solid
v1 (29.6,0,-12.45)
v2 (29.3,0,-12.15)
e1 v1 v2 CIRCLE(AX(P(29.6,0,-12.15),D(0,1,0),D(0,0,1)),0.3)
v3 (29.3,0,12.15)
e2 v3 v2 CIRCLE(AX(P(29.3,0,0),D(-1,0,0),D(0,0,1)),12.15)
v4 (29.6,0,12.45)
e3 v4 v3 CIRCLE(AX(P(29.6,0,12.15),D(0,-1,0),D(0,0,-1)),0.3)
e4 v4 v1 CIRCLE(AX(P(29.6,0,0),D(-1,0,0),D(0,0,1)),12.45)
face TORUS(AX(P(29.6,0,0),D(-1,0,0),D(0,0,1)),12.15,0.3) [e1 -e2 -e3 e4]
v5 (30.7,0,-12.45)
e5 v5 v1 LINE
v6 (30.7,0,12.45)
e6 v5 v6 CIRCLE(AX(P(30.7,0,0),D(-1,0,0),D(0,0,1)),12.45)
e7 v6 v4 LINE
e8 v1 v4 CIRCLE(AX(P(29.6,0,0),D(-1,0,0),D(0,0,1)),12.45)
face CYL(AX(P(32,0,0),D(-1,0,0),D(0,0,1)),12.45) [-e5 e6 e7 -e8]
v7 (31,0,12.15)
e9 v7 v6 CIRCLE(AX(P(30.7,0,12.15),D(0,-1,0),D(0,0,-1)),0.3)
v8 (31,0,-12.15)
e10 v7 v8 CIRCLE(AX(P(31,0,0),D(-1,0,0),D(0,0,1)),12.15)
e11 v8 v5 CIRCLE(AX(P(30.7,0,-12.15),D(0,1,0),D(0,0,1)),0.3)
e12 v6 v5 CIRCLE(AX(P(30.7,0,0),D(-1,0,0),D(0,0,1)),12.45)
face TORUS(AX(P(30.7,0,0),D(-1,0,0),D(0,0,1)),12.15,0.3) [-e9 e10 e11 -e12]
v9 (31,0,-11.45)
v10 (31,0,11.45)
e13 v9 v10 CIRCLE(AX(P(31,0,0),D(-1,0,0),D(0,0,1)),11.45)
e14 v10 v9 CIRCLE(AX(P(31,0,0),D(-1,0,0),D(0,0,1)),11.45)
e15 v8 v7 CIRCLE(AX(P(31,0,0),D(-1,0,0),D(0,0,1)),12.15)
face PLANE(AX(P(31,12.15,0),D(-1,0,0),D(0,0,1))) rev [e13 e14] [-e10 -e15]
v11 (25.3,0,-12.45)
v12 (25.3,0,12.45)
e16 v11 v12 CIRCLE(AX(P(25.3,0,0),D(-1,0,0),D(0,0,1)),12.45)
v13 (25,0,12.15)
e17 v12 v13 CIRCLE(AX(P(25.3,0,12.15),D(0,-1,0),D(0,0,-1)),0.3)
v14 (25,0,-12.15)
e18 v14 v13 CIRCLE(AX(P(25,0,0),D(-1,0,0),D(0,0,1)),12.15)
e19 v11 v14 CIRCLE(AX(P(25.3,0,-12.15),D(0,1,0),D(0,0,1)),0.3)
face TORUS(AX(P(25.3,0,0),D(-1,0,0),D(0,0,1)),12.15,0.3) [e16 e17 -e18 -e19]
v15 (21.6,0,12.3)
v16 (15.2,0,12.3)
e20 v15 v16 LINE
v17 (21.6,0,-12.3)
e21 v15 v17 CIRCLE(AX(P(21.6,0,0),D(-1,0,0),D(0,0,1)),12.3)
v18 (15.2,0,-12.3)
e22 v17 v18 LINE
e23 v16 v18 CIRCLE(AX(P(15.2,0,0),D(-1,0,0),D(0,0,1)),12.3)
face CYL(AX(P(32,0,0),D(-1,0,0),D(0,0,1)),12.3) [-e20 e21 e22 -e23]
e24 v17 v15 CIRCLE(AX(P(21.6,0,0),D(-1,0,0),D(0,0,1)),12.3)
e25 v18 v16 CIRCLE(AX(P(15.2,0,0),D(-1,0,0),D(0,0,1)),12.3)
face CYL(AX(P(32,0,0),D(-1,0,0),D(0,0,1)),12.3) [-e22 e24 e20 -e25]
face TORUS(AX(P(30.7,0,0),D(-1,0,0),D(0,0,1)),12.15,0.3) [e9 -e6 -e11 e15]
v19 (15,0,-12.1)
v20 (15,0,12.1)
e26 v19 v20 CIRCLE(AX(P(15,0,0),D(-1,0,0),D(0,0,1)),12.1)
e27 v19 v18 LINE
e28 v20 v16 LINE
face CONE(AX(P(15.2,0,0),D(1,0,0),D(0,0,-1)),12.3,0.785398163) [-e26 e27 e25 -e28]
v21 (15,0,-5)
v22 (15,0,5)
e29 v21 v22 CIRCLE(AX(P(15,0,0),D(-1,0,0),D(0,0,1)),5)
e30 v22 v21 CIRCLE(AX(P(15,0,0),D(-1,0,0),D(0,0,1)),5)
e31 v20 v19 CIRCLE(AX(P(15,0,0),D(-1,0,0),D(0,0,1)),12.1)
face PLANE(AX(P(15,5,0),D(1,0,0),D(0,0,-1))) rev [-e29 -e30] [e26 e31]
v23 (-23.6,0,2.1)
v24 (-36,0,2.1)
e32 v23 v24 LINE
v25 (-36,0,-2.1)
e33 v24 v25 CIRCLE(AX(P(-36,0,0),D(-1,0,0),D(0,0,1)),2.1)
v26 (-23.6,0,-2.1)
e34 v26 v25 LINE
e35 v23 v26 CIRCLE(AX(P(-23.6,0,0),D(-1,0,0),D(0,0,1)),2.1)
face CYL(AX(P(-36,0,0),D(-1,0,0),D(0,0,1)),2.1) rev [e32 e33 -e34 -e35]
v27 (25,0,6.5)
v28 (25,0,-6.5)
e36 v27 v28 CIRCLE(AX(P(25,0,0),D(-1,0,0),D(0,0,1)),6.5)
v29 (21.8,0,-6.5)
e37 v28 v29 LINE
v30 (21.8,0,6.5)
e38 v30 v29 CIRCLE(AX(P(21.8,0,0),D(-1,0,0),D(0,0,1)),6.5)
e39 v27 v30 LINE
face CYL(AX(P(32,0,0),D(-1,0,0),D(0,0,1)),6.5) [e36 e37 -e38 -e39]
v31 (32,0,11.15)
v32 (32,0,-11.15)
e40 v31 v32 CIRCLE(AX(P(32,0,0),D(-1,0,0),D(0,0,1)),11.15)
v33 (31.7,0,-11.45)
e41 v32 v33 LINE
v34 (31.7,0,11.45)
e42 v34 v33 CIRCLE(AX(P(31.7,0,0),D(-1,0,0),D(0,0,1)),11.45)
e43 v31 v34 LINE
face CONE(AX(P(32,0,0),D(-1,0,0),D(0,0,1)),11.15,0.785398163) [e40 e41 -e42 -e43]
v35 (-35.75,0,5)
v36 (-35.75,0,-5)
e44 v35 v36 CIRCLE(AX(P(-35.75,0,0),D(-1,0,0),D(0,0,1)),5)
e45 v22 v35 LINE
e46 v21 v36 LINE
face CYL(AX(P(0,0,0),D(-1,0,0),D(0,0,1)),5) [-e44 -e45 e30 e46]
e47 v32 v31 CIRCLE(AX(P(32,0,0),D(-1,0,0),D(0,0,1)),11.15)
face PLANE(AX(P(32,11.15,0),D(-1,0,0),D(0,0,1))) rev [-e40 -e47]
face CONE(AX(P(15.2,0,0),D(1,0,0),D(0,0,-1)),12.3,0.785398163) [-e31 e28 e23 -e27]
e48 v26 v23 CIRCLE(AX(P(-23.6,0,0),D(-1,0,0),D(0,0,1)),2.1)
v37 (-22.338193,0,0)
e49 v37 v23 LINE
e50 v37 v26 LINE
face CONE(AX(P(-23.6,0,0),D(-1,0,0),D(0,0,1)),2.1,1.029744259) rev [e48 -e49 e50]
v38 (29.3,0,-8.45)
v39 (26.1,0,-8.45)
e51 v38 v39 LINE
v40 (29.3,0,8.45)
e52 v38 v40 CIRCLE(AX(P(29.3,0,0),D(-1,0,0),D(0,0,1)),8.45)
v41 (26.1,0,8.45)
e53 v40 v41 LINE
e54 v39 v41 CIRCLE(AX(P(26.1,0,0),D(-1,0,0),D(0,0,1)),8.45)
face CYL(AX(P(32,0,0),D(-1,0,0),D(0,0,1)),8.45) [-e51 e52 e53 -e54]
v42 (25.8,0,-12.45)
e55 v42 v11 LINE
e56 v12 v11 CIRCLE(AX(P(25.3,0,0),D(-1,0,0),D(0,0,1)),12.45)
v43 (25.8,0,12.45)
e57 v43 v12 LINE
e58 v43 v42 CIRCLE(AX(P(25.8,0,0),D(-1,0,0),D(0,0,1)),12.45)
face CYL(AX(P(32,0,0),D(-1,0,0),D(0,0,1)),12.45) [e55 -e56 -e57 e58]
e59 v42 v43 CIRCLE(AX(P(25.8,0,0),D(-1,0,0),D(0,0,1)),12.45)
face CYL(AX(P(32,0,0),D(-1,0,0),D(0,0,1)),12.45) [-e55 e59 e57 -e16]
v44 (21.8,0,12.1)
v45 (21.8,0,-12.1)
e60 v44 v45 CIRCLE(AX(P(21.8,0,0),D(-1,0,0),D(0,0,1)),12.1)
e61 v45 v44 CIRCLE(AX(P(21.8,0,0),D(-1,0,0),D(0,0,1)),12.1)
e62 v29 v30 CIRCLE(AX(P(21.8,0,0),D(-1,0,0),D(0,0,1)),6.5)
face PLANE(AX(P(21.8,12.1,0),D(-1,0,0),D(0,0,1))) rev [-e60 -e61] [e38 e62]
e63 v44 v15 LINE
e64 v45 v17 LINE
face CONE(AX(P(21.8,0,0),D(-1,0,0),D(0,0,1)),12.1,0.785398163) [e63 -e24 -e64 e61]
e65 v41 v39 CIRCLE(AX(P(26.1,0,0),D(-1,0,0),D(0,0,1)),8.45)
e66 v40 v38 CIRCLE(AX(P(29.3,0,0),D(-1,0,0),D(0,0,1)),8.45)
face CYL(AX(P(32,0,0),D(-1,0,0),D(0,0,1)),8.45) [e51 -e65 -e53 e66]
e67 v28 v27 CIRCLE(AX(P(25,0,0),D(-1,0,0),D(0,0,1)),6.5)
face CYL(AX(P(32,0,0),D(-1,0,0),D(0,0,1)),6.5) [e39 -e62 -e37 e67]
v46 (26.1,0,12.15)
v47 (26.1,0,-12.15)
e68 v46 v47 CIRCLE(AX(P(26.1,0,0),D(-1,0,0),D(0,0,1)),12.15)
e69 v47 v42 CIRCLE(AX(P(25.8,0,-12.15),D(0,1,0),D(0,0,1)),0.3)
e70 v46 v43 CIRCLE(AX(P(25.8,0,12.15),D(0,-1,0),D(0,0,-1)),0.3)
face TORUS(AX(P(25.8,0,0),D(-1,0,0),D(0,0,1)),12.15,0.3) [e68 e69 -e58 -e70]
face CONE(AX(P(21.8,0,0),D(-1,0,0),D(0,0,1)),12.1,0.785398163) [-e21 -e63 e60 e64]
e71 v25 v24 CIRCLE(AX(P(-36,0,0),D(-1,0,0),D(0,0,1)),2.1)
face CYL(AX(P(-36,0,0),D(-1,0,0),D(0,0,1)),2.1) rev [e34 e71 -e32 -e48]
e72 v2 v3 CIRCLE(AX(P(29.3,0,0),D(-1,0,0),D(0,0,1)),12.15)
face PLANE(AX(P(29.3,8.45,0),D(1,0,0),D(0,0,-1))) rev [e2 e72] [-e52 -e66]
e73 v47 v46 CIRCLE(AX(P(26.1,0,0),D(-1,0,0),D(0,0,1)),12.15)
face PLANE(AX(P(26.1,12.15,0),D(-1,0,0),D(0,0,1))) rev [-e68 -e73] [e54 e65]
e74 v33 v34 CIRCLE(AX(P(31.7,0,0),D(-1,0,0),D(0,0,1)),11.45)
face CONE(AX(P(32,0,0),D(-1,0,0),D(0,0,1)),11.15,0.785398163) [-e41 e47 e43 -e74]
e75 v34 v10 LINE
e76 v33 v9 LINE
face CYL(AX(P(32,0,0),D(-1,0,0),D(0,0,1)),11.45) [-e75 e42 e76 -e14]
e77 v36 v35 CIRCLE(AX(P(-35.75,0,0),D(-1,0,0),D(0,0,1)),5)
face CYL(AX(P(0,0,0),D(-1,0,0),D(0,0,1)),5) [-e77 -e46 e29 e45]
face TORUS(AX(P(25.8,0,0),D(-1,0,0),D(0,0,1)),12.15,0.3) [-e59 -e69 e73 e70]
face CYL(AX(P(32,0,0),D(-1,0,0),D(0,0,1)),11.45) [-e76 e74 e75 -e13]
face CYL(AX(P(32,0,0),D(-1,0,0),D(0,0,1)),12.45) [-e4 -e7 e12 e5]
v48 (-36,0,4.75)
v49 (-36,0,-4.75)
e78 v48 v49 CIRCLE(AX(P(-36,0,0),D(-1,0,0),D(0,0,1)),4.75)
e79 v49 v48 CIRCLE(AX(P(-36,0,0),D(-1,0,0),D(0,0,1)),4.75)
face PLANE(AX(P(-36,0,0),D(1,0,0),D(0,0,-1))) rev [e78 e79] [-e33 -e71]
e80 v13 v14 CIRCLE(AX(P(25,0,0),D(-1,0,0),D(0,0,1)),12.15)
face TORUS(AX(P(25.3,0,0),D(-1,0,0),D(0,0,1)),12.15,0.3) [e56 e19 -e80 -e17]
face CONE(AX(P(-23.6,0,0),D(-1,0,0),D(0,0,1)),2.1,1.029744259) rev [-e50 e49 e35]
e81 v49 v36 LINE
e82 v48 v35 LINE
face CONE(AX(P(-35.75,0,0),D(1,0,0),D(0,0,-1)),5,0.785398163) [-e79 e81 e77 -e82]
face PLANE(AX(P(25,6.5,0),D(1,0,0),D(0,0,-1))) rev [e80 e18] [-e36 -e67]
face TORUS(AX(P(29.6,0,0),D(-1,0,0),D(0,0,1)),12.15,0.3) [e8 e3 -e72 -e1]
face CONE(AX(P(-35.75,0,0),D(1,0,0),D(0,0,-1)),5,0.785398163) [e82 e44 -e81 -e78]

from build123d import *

# Parameters (mm, degrees)
M5_TAPPED_HOLE1_D     = 4.2
M5_TAPPED_HOLE1_DEPTH = 12.4
M5_TAPPED_HOLE1_TIP   = 1.2618073


with BuildPart() as part:
    # Sketch1 → Revolve1 (revolve)
    with BuildSketch(Plane.XY, mode=Mode.PRIVATE) as revolve1_sk:
        Polygon((-36, 0), (-36, 4.75), (-35.75, 5), (0, 5), (0, 0), align=None)
    revolve(revolve1_sk.sketch.rotate(Axis((0, 0, 0), (-1, 0, 0)), 270), axis=Axis((0, 0, 0), (-1, 0, 0)))

    # Sketch2 → Revolve2 (revolve)
    with BuildSketch(Plane.XY, mode=Mode.PRIVATE) as revolve2_sk:
        with BuildLine():
            Line((0, 0), (0, 5))
            Line((0, 5), (15, 5))
            Line((15, 5), (15, 12.1))
            Line((15, 12.1), (15.2, 12.3))
            Line((15.2, 12.3), (21.6, 12.3))
            Line((21.6, 12.3), (21.8, 12.1))
            Line((21.8, 12.1), (21.8, 6.5))
            Line((21.8, 6.5), (25, 6.5))
            Line((25, 6.5), (25, 12.15))
            ThreePointArc((25, 12.15), (25.087867966, 12.362132034), (25.3, 12.45))
            Line((25.3, 12.45), (25.8, 12.45))
            ThreePointArc((25.8, 12.45), (26.012132034, 12.362132034), (26.1, 12.15))
            Line((26.1, 12.15), (26.1, 8.45))
            Line((26.1, 8.45), (29.3, 8.45))
            Line((29.3, 8.45), (29.3, 12.15))
            ThreePointArc((29.3, 12.15), (29.387867966, 12.362132034), (29.6, 12.45))
            Line((29.6, 12.45), (30.7, 12.45))
            ThreePointArc((30.7, 12.45), (30.912132034, 12.362132034), (31, 12.15))
            Line((31, 12.15), (31, 11.45))
            Line((31, 11.45), (31.7, 11.45))
            Line((31.7, 11.45), (32, 11.15))
            Line((32, 11.15), (32, 0))
            Line((32, 0), (0, 0))
        make_face()
    revolve(revolve2_sk.sketch.rotate(Axis((32, 0, 0), (-1, 0, 0)), 270), axis=Axis((32, 0, 0), (-1, 0, 0)))

    # M5 Tapped Hole1
    with Locations(Plane.ZY.offset(36)):
        with Locations((0, 0)):
            Hole(M5_TAPPED_HOLE1_D / 2, depth=M5_TAPPED_HOLE1_DEPTH)
            with Locations((0, 0, -(M5_TAPPED_HOLE1_DEPTH + M5_TAPPED_HOLE1_TIP / 2))):  # 118° drill point
                Cone(0, M5_TAPPED_HOLE1_D / 2, M5_TAPPED_HOLE1_TIP, mode=Mode.SUBTRACT)


solid = part.part
